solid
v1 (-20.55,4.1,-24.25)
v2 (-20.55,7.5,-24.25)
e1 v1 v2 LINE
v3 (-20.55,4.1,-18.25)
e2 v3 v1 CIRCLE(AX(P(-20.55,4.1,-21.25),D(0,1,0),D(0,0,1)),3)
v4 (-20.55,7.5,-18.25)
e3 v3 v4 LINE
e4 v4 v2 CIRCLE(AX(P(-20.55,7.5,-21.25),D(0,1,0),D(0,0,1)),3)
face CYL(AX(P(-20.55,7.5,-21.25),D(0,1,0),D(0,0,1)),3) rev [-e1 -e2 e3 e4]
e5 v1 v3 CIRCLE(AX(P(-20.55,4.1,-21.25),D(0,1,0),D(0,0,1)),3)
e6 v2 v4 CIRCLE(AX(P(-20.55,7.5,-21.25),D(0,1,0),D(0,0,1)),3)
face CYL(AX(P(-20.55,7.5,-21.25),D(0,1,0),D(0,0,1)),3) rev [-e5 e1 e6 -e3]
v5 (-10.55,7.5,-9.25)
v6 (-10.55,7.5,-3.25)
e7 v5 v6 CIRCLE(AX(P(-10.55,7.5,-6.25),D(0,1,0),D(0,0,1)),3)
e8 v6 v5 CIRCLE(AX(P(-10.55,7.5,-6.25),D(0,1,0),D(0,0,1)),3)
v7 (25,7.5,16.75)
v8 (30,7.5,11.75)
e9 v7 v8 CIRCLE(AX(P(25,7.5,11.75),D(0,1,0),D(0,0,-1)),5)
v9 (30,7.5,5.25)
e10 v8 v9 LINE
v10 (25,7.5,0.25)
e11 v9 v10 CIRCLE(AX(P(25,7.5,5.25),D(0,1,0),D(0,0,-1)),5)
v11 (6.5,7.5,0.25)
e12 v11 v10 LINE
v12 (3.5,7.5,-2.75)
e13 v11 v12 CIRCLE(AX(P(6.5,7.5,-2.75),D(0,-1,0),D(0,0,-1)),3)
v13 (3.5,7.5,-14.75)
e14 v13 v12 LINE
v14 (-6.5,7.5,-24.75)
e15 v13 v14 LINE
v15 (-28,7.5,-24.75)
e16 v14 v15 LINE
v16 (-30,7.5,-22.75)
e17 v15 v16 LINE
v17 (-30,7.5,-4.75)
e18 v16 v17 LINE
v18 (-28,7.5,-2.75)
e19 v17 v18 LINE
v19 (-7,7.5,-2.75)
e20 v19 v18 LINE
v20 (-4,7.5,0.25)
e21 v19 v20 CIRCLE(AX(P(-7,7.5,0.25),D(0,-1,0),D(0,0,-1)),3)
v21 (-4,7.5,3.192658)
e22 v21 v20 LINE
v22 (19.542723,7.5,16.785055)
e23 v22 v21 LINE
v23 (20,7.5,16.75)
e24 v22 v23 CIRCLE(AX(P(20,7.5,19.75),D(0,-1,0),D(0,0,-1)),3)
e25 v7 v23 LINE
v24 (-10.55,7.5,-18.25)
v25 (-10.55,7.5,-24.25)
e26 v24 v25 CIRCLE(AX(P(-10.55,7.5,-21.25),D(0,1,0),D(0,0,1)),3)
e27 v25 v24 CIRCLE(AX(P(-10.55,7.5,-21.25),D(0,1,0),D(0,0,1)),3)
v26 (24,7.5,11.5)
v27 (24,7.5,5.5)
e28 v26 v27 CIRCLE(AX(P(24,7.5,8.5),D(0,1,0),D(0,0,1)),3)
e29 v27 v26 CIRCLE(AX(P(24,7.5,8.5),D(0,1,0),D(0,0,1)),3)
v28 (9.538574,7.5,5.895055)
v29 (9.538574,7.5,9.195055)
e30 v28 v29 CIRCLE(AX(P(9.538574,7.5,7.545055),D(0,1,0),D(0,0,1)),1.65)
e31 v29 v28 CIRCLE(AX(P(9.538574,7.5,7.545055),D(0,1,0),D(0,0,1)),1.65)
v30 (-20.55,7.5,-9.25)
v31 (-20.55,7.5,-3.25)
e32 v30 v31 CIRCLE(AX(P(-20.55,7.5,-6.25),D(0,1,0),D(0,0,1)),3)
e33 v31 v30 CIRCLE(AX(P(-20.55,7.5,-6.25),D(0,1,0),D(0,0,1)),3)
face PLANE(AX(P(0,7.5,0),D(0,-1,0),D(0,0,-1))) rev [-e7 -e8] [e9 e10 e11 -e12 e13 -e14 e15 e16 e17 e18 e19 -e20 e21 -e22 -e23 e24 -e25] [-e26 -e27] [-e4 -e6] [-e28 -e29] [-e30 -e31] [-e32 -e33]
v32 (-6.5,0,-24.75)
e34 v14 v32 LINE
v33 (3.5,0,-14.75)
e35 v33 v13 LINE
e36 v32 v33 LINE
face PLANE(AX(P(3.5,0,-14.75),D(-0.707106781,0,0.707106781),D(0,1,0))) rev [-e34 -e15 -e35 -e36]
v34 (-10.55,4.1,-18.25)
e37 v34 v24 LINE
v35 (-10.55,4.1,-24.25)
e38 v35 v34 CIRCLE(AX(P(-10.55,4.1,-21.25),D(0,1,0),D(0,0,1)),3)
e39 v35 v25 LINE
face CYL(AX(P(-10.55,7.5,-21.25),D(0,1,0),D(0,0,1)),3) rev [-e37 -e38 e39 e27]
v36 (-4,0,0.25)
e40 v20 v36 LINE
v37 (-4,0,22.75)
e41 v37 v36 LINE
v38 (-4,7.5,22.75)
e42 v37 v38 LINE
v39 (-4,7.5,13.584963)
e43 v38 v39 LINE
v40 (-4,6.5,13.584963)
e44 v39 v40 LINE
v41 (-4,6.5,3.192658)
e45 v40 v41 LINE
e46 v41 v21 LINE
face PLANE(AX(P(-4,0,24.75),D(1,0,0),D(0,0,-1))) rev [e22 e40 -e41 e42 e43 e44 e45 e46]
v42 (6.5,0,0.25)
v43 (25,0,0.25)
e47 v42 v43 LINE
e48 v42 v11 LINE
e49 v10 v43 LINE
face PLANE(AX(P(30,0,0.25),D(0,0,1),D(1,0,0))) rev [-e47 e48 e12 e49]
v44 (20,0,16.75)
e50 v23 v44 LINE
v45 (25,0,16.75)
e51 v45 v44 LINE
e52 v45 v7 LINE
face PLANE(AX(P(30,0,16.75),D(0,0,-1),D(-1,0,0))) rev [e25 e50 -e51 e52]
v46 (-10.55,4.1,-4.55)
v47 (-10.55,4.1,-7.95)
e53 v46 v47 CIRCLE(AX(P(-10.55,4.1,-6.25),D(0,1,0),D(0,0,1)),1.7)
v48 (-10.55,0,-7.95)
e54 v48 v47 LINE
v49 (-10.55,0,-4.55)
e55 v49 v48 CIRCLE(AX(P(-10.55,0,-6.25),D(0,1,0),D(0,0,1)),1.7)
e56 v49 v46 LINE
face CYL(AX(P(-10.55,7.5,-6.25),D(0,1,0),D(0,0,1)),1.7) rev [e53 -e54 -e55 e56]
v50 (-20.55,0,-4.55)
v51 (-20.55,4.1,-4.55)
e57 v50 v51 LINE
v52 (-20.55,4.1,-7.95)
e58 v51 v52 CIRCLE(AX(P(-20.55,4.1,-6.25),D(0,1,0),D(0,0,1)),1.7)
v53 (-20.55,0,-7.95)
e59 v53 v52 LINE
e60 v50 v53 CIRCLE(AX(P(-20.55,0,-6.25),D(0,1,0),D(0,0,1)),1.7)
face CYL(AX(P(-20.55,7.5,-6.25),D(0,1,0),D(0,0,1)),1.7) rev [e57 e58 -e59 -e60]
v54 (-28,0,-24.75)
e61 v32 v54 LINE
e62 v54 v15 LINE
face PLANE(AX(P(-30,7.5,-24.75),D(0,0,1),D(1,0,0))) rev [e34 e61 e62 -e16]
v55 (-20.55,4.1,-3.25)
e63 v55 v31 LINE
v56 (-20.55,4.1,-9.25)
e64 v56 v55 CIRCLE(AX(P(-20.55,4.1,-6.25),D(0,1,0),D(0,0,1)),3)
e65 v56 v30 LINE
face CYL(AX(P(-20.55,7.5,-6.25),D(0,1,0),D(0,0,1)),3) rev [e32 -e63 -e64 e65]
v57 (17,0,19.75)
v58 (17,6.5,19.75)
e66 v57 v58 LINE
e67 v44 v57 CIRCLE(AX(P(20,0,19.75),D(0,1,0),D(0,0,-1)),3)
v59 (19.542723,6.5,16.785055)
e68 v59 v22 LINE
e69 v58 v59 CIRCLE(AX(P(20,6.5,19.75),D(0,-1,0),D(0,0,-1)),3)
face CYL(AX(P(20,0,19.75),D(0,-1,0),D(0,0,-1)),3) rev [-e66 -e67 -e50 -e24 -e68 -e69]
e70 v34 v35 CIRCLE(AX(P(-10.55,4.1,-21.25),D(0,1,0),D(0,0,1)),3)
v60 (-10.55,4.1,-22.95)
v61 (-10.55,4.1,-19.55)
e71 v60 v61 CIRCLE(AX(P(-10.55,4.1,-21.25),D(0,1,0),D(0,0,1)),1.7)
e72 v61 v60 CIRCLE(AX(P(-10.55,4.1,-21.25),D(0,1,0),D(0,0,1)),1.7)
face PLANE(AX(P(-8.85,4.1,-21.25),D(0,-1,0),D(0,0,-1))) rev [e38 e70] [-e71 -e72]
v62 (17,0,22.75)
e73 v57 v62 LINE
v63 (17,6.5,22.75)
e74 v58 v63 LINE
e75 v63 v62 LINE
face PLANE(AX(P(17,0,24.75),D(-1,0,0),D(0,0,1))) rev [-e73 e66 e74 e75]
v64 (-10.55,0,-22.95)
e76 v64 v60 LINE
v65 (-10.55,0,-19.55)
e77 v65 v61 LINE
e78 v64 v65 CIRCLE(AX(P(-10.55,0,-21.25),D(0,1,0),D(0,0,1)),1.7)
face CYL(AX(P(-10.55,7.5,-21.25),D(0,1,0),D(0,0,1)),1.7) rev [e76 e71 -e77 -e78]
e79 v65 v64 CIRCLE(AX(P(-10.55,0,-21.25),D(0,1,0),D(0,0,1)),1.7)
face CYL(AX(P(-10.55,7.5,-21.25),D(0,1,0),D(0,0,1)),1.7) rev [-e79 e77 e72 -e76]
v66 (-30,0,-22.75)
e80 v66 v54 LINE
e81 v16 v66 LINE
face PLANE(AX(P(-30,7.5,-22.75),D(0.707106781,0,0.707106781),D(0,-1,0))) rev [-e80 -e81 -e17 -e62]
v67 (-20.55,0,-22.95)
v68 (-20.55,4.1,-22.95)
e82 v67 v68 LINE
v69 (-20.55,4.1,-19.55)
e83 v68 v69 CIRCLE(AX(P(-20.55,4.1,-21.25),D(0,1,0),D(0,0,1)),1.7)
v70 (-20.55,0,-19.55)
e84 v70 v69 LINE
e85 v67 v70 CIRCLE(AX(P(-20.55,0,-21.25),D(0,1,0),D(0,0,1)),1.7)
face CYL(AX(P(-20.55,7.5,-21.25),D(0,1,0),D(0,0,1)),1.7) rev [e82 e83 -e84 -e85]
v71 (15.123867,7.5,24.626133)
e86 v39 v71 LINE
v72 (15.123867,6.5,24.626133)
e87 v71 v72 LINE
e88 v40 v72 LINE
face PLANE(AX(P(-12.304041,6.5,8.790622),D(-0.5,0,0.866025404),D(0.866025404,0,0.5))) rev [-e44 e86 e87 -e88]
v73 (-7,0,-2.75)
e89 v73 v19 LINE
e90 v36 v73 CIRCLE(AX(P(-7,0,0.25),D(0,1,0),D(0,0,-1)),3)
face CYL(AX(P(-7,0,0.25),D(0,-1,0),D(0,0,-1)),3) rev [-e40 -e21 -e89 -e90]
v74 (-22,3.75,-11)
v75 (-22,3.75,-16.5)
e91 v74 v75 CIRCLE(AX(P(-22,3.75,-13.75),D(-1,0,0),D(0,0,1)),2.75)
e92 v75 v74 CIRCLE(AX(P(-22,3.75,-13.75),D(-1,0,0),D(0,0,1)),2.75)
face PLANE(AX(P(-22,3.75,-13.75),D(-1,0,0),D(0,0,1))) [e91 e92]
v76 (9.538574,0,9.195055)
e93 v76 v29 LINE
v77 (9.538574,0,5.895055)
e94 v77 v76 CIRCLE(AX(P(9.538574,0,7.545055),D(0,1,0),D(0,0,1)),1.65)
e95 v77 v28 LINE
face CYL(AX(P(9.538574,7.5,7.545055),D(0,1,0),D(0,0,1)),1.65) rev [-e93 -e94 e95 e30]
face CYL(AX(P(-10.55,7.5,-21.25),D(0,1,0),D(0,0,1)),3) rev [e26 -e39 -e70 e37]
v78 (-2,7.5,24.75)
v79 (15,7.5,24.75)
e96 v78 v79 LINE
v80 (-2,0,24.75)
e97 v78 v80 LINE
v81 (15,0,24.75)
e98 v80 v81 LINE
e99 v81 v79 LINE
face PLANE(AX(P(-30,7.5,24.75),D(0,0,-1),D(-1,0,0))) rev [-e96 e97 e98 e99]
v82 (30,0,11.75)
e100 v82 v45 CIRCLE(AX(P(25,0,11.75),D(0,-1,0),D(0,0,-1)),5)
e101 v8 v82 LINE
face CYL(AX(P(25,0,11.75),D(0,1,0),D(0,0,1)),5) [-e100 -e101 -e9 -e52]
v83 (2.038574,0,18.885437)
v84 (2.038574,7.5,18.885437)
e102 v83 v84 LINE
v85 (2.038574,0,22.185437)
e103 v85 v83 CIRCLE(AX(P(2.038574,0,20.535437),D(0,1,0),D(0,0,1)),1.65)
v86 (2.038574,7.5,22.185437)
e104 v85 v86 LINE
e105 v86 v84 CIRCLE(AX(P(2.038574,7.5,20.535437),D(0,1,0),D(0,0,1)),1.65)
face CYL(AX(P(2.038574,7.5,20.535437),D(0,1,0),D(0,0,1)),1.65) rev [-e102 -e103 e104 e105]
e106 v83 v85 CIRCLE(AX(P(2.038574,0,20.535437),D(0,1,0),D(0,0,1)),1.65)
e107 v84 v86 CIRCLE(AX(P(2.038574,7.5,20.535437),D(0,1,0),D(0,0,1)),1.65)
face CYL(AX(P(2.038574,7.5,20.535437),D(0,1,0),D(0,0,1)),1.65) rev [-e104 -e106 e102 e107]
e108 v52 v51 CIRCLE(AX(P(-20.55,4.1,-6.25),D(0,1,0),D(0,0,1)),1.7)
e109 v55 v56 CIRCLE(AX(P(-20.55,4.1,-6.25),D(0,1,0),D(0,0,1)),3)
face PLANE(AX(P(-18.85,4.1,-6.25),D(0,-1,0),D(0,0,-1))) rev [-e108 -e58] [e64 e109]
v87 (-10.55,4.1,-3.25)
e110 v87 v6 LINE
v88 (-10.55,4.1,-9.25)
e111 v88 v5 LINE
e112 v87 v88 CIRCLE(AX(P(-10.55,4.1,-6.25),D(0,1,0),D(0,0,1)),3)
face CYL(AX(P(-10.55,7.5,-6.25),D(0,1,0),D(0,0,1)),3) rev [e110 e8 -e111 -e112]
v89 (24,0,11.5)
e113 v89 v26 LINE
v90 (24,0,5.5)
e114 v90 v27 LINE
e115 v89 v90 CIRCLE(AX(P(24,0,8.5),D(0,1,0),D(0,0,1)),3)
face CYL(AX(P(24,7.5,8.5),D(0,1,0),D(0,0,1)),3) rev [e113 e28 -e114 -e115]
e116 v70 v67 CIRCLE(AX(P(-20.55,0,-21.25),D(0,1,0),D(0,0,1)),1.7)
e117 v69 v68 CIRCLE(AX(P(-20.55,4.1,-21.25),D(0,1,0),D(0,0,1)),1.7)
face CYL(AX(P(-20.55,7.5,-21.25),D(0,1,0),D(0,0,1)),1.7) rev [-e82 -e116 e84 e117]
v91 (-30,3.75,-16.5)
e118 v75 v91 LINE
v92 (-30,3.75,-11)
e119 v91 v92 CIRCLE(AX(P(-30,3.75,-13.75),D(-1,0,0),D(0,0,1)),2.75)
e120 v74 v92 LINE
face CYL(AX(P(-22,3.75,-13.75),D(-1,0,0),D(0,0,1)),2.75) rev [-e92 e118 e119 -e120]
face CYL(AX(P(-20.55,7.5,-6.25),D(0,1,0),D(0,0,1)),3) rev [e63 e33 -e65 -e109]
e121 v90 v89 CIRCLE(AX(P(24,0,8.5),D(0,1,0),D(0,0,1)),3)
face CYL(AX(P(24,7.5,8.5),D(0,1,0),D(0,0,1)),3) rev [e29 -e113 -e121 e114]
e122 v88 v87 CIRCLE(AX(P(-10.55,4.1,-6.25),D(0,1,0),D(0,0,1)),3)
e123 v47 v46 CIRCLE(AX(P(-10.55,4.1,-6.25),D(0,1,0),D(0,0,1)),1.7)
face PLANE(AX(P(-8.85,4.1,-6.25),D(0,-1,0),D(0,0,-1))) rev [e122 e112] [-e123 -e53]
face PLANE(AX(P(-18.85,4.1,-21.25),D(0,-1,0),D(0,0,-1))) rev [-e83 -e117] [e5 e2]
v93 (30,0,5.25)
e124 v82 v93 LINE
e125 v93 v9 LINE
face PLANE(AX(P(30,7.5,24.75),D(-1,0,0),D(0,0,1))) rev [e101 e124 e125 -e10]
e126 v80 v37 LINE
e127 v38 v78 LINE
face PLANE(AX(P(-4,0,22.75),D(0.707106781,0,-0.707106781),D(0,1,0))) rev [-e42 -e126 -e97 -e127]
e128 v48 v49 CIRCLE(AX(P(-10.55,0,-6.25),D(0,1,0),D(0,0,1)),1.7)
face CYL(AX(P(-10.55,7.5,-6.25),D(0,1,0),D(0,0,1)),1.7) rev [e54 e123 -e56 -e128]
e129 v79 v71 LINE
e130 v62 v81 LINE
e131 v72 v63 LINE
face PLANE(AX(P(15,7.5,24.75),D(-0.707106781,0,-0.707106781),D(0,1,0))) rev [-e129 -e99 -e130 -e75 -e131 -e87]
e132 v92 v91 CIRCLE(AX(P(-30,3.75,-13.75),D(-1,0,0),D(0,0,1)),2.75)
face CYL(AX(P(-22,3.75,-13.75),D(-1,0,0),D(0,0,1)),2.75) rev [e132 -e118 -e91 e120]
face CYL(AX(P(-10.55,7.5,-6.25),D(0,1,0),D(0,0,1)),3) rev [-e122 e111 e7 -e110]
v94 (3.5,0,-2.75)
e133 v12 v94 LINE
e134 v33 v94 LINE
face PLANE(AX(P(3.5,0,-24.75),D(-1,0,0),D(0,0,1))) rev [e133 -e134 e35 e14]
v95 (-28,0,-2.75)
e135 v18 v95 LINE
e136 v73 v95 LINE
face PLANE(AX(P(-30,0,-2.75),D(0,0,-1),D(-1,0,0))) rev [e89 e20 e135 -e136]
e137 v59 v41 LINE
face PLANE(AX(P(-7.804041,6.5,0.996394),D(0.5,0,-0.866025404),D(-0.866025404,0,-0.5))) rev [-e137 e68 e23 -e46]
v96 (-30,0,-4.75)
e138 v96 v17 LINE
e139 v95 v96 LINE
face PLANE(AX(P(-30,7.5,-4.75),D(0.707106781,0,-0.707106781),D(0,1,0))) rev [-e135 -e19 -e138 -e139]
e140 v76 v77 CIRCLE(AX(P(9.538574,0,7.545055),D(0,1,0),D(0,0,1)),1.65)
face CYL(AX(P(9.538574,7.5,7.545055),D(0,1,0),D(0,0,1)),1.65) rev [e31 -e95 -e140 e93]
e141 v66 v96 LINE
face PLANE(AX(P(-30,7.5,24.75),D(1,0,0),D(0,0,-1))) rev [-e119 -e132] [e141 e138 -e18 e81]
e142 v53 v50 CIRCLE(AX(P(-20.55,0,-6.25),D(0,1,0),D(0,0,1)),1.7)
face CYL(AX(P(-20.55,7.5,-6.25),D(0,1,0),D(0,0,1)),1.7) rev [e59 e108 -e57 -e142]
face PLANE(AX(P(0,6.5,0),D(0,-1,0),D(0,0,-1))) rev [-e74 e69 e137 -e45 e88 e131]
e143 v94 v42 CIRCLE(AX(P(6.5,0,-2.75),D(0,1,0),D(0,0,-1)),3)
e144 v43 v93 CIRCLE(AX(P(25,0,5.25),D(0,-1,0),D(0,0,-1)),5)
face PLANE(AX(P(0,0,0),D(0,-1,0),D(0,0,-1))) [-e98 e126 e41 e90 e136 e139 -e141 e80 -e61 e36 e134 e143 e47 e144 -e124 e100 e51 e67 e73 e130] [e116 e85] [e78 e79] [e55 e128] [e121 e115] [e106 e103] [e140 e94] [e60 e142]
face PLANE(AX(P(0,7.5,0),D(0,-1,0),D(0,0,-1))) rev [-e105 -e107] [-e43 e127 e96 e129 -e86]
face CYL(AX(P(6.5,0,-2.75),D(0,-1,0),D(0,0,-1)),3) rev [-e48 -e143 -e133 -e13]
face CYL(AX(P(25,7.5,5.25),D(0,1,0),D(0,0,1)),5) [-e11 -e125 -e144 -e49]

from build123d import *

# Parameters (mm, degrees)
SKETCH1_W                                          = 60
SKETCH1_H                                          = 49.5
BOSS_EXTRUDE1_DEPTH                                = 7.5
SKETCH2_W                                          = 26.5
SKETCH2_H                                          = 25
SKETCH2_W_2                                        = 13
SKETCH2_H_2                                        = 8
SKETCH2_W_3                                        = 26
SKETCH2_H_3                                        = 27.5
CUT_EXTRUDE1_DEPTH                                 = 40.60823778
HOLE_WIZARD_SOCKET_HEAD_CAP_SCREW_TYPE_D           = 3.4
HOLE_WIZARD_SOCKET_HEAD_CAP_SCREW_TYPE_CBORE_D     = 6
HOLE_WIZARD_SOCKET_HEAD_CAP_SCREW_TYPE_CBORE_DEPTH = 3.4
F_6_0_6_DIAMETER_HOLE1_D                           = 6
CUT_EXTRUDE2_DEPTH                                 = 1
FILLET1_R                                          = 5
CHAMFER1_SIZE                                      = 10
CHAMFER2_SIZE                                      = 2
FILLET2_R                                          = 3
M4_TAPPED_HOLE1_D                                  = 3.3
SKETCH10_R                                         = 2.75
CUT_EXTRUDE3_DEPTH                                 = 8


with BuildPart() as part:
    # Sketch1 → Boss-Extrude1 (new body)
    with BuildSketch(Plane(origin=(0, 0, 0), x_dir=(1, 0, 0), z_dir=(0, 1, 0))):
        Rectangle(SKETCH1_W, SKETCH1_H)
    extrude(amount=BOSS_EXTRUDE1_DEPTH)

    # Sketch2 → Cut-Extrude1 (cut, through all)
    with BuildSketch(Plane(origin=(0, 7.5, 0), x_dir=(1, 0, 0), z_dir=(0, 1, 0))):
        with Locations((16.75, 12.25)):
            Rectangle(SKETCH2_W, SKETCH2_H)
        with Locations((23.5, -20.75)):
            Rectangle(SKETCH2_W_2, SKETCH2_H_2)
        with Locations((-17, -11)):
            Rectangle(SKETCH2_W_3, SKETCH2_H_3)
    extrude(amount=-CUT_EXTRUDE1_DEPTH, mode=Mode.SUBTRACT)

    # Hole wizard: socket head cap screw, type 1 (through all)
    with Locations(Plane(origin=(0, 7.5, 0), x_dir=(1, 0, 0), z_dir=(0, 1, 0))):
        with Locations((-10.55, 21.25), (-20.55, 21.25), (-20.55, 6.25), (-10.55, 6.25)):
            CounterBoreHole(HOLE_WIZARD_SOCKET_HEAD_CAP_SCREW_TYPE_D / 2, HOLE_WIZARD_SOCKET_HEAD_CAP_SCREW_TYPE_CBORE_D / 2, HOLE_WIZARD_SOCKET_HEAD_CAP_SCREW_TYPE_CBORE_DEPTH)

    # Ø6.0 (6) Diameter Hole1 (through all)
    with Locations(Plane(origin=(0, 7.5, 0), x_dir=(1, 0, 0), z_dir=(0, 1, 0))):
        with Locations((24, -8.5)):
            Hole(F_6_0_6_DIAMETER_HOLE1_D / 2)

    # Sketch7 → Cut-Extrude2 (cut)
    with BuildSketch(Plane(origin=(0, 7.5, 0), x_dir=(1, 0, 0), z_dir=(0, 1, 0))):
        Polygon((-12.304041346, -8.790622211), (20.302775541, -27.616176718), (24.802775541, -19.821948084), (-7.804041346, -0.996393577), align=None)
    extrude(amount=-CUT_EXTRUDE2_DEPTH, mode=Mode.SUBTRACT)

    # Fillet1
    fillet1_edges = [part.edges().sort_by_distance(p)[0] for p in [
        (30, 3.75, 16.75),
        (30, 3.75, 0.25),
    ]]
    fillet(fillet1_edges, radius=FILLET1_R)

    # Chamfer1
    chamfer1_edges = [part.edges().sort_by_distance(p)[0] for p in [
        (3.5, 3.75, -24.75),
    ]]
    chamfer(chamfer1_edges, length=CHAMFER1_SIZE)

    # Chamfer2
    chamfer2_edges = [part.edges().sort_by_distance(p)[0] for p in [
        (17, 3.25, 24.75),
        (-4, 3.75, 24.75),
        (-30, 3.75, -2.75),
        (-30, 3.75, -24.75),
    ]]
    chamfer(chamfer2_edges, length=CHAMFER2_SIZE)

    # Fillet2
    fillet2_edges = [part.edges().sort_by_distance(p)[0] for p in [
        (3.5, 3.75, 0.25),
        (17, 3.25, 16.75),
        (-4, 3.75, -2.75),
    ]]
    fillet(fillet2_edges, radius=FILLET2_R)

    # M4 Tapped Hole1 (through all)
    with Locations(Plane(origin=(0, 7.5, 0), x_dir=(1, 0, 0), z_dir=(0, 1, 0))):
        with Locations((9.538573783, -7.545055475), (2.038573783, -20.535436532)):
            Hole(M4_TAPPED_HOLE1_D / 2)

    # Sketch10 → Cut-Extrude3 (cut)
    with BuildSketch(Plane.ZY.offset(30)):
        with Locations((-13.75, 3.75)):
            Circle(SKETCH10_R)
    extrude(amount=-CUT_EXTRUDE3_DEPTH, mode=Mode.SUBTRACT)


solid = part.part
